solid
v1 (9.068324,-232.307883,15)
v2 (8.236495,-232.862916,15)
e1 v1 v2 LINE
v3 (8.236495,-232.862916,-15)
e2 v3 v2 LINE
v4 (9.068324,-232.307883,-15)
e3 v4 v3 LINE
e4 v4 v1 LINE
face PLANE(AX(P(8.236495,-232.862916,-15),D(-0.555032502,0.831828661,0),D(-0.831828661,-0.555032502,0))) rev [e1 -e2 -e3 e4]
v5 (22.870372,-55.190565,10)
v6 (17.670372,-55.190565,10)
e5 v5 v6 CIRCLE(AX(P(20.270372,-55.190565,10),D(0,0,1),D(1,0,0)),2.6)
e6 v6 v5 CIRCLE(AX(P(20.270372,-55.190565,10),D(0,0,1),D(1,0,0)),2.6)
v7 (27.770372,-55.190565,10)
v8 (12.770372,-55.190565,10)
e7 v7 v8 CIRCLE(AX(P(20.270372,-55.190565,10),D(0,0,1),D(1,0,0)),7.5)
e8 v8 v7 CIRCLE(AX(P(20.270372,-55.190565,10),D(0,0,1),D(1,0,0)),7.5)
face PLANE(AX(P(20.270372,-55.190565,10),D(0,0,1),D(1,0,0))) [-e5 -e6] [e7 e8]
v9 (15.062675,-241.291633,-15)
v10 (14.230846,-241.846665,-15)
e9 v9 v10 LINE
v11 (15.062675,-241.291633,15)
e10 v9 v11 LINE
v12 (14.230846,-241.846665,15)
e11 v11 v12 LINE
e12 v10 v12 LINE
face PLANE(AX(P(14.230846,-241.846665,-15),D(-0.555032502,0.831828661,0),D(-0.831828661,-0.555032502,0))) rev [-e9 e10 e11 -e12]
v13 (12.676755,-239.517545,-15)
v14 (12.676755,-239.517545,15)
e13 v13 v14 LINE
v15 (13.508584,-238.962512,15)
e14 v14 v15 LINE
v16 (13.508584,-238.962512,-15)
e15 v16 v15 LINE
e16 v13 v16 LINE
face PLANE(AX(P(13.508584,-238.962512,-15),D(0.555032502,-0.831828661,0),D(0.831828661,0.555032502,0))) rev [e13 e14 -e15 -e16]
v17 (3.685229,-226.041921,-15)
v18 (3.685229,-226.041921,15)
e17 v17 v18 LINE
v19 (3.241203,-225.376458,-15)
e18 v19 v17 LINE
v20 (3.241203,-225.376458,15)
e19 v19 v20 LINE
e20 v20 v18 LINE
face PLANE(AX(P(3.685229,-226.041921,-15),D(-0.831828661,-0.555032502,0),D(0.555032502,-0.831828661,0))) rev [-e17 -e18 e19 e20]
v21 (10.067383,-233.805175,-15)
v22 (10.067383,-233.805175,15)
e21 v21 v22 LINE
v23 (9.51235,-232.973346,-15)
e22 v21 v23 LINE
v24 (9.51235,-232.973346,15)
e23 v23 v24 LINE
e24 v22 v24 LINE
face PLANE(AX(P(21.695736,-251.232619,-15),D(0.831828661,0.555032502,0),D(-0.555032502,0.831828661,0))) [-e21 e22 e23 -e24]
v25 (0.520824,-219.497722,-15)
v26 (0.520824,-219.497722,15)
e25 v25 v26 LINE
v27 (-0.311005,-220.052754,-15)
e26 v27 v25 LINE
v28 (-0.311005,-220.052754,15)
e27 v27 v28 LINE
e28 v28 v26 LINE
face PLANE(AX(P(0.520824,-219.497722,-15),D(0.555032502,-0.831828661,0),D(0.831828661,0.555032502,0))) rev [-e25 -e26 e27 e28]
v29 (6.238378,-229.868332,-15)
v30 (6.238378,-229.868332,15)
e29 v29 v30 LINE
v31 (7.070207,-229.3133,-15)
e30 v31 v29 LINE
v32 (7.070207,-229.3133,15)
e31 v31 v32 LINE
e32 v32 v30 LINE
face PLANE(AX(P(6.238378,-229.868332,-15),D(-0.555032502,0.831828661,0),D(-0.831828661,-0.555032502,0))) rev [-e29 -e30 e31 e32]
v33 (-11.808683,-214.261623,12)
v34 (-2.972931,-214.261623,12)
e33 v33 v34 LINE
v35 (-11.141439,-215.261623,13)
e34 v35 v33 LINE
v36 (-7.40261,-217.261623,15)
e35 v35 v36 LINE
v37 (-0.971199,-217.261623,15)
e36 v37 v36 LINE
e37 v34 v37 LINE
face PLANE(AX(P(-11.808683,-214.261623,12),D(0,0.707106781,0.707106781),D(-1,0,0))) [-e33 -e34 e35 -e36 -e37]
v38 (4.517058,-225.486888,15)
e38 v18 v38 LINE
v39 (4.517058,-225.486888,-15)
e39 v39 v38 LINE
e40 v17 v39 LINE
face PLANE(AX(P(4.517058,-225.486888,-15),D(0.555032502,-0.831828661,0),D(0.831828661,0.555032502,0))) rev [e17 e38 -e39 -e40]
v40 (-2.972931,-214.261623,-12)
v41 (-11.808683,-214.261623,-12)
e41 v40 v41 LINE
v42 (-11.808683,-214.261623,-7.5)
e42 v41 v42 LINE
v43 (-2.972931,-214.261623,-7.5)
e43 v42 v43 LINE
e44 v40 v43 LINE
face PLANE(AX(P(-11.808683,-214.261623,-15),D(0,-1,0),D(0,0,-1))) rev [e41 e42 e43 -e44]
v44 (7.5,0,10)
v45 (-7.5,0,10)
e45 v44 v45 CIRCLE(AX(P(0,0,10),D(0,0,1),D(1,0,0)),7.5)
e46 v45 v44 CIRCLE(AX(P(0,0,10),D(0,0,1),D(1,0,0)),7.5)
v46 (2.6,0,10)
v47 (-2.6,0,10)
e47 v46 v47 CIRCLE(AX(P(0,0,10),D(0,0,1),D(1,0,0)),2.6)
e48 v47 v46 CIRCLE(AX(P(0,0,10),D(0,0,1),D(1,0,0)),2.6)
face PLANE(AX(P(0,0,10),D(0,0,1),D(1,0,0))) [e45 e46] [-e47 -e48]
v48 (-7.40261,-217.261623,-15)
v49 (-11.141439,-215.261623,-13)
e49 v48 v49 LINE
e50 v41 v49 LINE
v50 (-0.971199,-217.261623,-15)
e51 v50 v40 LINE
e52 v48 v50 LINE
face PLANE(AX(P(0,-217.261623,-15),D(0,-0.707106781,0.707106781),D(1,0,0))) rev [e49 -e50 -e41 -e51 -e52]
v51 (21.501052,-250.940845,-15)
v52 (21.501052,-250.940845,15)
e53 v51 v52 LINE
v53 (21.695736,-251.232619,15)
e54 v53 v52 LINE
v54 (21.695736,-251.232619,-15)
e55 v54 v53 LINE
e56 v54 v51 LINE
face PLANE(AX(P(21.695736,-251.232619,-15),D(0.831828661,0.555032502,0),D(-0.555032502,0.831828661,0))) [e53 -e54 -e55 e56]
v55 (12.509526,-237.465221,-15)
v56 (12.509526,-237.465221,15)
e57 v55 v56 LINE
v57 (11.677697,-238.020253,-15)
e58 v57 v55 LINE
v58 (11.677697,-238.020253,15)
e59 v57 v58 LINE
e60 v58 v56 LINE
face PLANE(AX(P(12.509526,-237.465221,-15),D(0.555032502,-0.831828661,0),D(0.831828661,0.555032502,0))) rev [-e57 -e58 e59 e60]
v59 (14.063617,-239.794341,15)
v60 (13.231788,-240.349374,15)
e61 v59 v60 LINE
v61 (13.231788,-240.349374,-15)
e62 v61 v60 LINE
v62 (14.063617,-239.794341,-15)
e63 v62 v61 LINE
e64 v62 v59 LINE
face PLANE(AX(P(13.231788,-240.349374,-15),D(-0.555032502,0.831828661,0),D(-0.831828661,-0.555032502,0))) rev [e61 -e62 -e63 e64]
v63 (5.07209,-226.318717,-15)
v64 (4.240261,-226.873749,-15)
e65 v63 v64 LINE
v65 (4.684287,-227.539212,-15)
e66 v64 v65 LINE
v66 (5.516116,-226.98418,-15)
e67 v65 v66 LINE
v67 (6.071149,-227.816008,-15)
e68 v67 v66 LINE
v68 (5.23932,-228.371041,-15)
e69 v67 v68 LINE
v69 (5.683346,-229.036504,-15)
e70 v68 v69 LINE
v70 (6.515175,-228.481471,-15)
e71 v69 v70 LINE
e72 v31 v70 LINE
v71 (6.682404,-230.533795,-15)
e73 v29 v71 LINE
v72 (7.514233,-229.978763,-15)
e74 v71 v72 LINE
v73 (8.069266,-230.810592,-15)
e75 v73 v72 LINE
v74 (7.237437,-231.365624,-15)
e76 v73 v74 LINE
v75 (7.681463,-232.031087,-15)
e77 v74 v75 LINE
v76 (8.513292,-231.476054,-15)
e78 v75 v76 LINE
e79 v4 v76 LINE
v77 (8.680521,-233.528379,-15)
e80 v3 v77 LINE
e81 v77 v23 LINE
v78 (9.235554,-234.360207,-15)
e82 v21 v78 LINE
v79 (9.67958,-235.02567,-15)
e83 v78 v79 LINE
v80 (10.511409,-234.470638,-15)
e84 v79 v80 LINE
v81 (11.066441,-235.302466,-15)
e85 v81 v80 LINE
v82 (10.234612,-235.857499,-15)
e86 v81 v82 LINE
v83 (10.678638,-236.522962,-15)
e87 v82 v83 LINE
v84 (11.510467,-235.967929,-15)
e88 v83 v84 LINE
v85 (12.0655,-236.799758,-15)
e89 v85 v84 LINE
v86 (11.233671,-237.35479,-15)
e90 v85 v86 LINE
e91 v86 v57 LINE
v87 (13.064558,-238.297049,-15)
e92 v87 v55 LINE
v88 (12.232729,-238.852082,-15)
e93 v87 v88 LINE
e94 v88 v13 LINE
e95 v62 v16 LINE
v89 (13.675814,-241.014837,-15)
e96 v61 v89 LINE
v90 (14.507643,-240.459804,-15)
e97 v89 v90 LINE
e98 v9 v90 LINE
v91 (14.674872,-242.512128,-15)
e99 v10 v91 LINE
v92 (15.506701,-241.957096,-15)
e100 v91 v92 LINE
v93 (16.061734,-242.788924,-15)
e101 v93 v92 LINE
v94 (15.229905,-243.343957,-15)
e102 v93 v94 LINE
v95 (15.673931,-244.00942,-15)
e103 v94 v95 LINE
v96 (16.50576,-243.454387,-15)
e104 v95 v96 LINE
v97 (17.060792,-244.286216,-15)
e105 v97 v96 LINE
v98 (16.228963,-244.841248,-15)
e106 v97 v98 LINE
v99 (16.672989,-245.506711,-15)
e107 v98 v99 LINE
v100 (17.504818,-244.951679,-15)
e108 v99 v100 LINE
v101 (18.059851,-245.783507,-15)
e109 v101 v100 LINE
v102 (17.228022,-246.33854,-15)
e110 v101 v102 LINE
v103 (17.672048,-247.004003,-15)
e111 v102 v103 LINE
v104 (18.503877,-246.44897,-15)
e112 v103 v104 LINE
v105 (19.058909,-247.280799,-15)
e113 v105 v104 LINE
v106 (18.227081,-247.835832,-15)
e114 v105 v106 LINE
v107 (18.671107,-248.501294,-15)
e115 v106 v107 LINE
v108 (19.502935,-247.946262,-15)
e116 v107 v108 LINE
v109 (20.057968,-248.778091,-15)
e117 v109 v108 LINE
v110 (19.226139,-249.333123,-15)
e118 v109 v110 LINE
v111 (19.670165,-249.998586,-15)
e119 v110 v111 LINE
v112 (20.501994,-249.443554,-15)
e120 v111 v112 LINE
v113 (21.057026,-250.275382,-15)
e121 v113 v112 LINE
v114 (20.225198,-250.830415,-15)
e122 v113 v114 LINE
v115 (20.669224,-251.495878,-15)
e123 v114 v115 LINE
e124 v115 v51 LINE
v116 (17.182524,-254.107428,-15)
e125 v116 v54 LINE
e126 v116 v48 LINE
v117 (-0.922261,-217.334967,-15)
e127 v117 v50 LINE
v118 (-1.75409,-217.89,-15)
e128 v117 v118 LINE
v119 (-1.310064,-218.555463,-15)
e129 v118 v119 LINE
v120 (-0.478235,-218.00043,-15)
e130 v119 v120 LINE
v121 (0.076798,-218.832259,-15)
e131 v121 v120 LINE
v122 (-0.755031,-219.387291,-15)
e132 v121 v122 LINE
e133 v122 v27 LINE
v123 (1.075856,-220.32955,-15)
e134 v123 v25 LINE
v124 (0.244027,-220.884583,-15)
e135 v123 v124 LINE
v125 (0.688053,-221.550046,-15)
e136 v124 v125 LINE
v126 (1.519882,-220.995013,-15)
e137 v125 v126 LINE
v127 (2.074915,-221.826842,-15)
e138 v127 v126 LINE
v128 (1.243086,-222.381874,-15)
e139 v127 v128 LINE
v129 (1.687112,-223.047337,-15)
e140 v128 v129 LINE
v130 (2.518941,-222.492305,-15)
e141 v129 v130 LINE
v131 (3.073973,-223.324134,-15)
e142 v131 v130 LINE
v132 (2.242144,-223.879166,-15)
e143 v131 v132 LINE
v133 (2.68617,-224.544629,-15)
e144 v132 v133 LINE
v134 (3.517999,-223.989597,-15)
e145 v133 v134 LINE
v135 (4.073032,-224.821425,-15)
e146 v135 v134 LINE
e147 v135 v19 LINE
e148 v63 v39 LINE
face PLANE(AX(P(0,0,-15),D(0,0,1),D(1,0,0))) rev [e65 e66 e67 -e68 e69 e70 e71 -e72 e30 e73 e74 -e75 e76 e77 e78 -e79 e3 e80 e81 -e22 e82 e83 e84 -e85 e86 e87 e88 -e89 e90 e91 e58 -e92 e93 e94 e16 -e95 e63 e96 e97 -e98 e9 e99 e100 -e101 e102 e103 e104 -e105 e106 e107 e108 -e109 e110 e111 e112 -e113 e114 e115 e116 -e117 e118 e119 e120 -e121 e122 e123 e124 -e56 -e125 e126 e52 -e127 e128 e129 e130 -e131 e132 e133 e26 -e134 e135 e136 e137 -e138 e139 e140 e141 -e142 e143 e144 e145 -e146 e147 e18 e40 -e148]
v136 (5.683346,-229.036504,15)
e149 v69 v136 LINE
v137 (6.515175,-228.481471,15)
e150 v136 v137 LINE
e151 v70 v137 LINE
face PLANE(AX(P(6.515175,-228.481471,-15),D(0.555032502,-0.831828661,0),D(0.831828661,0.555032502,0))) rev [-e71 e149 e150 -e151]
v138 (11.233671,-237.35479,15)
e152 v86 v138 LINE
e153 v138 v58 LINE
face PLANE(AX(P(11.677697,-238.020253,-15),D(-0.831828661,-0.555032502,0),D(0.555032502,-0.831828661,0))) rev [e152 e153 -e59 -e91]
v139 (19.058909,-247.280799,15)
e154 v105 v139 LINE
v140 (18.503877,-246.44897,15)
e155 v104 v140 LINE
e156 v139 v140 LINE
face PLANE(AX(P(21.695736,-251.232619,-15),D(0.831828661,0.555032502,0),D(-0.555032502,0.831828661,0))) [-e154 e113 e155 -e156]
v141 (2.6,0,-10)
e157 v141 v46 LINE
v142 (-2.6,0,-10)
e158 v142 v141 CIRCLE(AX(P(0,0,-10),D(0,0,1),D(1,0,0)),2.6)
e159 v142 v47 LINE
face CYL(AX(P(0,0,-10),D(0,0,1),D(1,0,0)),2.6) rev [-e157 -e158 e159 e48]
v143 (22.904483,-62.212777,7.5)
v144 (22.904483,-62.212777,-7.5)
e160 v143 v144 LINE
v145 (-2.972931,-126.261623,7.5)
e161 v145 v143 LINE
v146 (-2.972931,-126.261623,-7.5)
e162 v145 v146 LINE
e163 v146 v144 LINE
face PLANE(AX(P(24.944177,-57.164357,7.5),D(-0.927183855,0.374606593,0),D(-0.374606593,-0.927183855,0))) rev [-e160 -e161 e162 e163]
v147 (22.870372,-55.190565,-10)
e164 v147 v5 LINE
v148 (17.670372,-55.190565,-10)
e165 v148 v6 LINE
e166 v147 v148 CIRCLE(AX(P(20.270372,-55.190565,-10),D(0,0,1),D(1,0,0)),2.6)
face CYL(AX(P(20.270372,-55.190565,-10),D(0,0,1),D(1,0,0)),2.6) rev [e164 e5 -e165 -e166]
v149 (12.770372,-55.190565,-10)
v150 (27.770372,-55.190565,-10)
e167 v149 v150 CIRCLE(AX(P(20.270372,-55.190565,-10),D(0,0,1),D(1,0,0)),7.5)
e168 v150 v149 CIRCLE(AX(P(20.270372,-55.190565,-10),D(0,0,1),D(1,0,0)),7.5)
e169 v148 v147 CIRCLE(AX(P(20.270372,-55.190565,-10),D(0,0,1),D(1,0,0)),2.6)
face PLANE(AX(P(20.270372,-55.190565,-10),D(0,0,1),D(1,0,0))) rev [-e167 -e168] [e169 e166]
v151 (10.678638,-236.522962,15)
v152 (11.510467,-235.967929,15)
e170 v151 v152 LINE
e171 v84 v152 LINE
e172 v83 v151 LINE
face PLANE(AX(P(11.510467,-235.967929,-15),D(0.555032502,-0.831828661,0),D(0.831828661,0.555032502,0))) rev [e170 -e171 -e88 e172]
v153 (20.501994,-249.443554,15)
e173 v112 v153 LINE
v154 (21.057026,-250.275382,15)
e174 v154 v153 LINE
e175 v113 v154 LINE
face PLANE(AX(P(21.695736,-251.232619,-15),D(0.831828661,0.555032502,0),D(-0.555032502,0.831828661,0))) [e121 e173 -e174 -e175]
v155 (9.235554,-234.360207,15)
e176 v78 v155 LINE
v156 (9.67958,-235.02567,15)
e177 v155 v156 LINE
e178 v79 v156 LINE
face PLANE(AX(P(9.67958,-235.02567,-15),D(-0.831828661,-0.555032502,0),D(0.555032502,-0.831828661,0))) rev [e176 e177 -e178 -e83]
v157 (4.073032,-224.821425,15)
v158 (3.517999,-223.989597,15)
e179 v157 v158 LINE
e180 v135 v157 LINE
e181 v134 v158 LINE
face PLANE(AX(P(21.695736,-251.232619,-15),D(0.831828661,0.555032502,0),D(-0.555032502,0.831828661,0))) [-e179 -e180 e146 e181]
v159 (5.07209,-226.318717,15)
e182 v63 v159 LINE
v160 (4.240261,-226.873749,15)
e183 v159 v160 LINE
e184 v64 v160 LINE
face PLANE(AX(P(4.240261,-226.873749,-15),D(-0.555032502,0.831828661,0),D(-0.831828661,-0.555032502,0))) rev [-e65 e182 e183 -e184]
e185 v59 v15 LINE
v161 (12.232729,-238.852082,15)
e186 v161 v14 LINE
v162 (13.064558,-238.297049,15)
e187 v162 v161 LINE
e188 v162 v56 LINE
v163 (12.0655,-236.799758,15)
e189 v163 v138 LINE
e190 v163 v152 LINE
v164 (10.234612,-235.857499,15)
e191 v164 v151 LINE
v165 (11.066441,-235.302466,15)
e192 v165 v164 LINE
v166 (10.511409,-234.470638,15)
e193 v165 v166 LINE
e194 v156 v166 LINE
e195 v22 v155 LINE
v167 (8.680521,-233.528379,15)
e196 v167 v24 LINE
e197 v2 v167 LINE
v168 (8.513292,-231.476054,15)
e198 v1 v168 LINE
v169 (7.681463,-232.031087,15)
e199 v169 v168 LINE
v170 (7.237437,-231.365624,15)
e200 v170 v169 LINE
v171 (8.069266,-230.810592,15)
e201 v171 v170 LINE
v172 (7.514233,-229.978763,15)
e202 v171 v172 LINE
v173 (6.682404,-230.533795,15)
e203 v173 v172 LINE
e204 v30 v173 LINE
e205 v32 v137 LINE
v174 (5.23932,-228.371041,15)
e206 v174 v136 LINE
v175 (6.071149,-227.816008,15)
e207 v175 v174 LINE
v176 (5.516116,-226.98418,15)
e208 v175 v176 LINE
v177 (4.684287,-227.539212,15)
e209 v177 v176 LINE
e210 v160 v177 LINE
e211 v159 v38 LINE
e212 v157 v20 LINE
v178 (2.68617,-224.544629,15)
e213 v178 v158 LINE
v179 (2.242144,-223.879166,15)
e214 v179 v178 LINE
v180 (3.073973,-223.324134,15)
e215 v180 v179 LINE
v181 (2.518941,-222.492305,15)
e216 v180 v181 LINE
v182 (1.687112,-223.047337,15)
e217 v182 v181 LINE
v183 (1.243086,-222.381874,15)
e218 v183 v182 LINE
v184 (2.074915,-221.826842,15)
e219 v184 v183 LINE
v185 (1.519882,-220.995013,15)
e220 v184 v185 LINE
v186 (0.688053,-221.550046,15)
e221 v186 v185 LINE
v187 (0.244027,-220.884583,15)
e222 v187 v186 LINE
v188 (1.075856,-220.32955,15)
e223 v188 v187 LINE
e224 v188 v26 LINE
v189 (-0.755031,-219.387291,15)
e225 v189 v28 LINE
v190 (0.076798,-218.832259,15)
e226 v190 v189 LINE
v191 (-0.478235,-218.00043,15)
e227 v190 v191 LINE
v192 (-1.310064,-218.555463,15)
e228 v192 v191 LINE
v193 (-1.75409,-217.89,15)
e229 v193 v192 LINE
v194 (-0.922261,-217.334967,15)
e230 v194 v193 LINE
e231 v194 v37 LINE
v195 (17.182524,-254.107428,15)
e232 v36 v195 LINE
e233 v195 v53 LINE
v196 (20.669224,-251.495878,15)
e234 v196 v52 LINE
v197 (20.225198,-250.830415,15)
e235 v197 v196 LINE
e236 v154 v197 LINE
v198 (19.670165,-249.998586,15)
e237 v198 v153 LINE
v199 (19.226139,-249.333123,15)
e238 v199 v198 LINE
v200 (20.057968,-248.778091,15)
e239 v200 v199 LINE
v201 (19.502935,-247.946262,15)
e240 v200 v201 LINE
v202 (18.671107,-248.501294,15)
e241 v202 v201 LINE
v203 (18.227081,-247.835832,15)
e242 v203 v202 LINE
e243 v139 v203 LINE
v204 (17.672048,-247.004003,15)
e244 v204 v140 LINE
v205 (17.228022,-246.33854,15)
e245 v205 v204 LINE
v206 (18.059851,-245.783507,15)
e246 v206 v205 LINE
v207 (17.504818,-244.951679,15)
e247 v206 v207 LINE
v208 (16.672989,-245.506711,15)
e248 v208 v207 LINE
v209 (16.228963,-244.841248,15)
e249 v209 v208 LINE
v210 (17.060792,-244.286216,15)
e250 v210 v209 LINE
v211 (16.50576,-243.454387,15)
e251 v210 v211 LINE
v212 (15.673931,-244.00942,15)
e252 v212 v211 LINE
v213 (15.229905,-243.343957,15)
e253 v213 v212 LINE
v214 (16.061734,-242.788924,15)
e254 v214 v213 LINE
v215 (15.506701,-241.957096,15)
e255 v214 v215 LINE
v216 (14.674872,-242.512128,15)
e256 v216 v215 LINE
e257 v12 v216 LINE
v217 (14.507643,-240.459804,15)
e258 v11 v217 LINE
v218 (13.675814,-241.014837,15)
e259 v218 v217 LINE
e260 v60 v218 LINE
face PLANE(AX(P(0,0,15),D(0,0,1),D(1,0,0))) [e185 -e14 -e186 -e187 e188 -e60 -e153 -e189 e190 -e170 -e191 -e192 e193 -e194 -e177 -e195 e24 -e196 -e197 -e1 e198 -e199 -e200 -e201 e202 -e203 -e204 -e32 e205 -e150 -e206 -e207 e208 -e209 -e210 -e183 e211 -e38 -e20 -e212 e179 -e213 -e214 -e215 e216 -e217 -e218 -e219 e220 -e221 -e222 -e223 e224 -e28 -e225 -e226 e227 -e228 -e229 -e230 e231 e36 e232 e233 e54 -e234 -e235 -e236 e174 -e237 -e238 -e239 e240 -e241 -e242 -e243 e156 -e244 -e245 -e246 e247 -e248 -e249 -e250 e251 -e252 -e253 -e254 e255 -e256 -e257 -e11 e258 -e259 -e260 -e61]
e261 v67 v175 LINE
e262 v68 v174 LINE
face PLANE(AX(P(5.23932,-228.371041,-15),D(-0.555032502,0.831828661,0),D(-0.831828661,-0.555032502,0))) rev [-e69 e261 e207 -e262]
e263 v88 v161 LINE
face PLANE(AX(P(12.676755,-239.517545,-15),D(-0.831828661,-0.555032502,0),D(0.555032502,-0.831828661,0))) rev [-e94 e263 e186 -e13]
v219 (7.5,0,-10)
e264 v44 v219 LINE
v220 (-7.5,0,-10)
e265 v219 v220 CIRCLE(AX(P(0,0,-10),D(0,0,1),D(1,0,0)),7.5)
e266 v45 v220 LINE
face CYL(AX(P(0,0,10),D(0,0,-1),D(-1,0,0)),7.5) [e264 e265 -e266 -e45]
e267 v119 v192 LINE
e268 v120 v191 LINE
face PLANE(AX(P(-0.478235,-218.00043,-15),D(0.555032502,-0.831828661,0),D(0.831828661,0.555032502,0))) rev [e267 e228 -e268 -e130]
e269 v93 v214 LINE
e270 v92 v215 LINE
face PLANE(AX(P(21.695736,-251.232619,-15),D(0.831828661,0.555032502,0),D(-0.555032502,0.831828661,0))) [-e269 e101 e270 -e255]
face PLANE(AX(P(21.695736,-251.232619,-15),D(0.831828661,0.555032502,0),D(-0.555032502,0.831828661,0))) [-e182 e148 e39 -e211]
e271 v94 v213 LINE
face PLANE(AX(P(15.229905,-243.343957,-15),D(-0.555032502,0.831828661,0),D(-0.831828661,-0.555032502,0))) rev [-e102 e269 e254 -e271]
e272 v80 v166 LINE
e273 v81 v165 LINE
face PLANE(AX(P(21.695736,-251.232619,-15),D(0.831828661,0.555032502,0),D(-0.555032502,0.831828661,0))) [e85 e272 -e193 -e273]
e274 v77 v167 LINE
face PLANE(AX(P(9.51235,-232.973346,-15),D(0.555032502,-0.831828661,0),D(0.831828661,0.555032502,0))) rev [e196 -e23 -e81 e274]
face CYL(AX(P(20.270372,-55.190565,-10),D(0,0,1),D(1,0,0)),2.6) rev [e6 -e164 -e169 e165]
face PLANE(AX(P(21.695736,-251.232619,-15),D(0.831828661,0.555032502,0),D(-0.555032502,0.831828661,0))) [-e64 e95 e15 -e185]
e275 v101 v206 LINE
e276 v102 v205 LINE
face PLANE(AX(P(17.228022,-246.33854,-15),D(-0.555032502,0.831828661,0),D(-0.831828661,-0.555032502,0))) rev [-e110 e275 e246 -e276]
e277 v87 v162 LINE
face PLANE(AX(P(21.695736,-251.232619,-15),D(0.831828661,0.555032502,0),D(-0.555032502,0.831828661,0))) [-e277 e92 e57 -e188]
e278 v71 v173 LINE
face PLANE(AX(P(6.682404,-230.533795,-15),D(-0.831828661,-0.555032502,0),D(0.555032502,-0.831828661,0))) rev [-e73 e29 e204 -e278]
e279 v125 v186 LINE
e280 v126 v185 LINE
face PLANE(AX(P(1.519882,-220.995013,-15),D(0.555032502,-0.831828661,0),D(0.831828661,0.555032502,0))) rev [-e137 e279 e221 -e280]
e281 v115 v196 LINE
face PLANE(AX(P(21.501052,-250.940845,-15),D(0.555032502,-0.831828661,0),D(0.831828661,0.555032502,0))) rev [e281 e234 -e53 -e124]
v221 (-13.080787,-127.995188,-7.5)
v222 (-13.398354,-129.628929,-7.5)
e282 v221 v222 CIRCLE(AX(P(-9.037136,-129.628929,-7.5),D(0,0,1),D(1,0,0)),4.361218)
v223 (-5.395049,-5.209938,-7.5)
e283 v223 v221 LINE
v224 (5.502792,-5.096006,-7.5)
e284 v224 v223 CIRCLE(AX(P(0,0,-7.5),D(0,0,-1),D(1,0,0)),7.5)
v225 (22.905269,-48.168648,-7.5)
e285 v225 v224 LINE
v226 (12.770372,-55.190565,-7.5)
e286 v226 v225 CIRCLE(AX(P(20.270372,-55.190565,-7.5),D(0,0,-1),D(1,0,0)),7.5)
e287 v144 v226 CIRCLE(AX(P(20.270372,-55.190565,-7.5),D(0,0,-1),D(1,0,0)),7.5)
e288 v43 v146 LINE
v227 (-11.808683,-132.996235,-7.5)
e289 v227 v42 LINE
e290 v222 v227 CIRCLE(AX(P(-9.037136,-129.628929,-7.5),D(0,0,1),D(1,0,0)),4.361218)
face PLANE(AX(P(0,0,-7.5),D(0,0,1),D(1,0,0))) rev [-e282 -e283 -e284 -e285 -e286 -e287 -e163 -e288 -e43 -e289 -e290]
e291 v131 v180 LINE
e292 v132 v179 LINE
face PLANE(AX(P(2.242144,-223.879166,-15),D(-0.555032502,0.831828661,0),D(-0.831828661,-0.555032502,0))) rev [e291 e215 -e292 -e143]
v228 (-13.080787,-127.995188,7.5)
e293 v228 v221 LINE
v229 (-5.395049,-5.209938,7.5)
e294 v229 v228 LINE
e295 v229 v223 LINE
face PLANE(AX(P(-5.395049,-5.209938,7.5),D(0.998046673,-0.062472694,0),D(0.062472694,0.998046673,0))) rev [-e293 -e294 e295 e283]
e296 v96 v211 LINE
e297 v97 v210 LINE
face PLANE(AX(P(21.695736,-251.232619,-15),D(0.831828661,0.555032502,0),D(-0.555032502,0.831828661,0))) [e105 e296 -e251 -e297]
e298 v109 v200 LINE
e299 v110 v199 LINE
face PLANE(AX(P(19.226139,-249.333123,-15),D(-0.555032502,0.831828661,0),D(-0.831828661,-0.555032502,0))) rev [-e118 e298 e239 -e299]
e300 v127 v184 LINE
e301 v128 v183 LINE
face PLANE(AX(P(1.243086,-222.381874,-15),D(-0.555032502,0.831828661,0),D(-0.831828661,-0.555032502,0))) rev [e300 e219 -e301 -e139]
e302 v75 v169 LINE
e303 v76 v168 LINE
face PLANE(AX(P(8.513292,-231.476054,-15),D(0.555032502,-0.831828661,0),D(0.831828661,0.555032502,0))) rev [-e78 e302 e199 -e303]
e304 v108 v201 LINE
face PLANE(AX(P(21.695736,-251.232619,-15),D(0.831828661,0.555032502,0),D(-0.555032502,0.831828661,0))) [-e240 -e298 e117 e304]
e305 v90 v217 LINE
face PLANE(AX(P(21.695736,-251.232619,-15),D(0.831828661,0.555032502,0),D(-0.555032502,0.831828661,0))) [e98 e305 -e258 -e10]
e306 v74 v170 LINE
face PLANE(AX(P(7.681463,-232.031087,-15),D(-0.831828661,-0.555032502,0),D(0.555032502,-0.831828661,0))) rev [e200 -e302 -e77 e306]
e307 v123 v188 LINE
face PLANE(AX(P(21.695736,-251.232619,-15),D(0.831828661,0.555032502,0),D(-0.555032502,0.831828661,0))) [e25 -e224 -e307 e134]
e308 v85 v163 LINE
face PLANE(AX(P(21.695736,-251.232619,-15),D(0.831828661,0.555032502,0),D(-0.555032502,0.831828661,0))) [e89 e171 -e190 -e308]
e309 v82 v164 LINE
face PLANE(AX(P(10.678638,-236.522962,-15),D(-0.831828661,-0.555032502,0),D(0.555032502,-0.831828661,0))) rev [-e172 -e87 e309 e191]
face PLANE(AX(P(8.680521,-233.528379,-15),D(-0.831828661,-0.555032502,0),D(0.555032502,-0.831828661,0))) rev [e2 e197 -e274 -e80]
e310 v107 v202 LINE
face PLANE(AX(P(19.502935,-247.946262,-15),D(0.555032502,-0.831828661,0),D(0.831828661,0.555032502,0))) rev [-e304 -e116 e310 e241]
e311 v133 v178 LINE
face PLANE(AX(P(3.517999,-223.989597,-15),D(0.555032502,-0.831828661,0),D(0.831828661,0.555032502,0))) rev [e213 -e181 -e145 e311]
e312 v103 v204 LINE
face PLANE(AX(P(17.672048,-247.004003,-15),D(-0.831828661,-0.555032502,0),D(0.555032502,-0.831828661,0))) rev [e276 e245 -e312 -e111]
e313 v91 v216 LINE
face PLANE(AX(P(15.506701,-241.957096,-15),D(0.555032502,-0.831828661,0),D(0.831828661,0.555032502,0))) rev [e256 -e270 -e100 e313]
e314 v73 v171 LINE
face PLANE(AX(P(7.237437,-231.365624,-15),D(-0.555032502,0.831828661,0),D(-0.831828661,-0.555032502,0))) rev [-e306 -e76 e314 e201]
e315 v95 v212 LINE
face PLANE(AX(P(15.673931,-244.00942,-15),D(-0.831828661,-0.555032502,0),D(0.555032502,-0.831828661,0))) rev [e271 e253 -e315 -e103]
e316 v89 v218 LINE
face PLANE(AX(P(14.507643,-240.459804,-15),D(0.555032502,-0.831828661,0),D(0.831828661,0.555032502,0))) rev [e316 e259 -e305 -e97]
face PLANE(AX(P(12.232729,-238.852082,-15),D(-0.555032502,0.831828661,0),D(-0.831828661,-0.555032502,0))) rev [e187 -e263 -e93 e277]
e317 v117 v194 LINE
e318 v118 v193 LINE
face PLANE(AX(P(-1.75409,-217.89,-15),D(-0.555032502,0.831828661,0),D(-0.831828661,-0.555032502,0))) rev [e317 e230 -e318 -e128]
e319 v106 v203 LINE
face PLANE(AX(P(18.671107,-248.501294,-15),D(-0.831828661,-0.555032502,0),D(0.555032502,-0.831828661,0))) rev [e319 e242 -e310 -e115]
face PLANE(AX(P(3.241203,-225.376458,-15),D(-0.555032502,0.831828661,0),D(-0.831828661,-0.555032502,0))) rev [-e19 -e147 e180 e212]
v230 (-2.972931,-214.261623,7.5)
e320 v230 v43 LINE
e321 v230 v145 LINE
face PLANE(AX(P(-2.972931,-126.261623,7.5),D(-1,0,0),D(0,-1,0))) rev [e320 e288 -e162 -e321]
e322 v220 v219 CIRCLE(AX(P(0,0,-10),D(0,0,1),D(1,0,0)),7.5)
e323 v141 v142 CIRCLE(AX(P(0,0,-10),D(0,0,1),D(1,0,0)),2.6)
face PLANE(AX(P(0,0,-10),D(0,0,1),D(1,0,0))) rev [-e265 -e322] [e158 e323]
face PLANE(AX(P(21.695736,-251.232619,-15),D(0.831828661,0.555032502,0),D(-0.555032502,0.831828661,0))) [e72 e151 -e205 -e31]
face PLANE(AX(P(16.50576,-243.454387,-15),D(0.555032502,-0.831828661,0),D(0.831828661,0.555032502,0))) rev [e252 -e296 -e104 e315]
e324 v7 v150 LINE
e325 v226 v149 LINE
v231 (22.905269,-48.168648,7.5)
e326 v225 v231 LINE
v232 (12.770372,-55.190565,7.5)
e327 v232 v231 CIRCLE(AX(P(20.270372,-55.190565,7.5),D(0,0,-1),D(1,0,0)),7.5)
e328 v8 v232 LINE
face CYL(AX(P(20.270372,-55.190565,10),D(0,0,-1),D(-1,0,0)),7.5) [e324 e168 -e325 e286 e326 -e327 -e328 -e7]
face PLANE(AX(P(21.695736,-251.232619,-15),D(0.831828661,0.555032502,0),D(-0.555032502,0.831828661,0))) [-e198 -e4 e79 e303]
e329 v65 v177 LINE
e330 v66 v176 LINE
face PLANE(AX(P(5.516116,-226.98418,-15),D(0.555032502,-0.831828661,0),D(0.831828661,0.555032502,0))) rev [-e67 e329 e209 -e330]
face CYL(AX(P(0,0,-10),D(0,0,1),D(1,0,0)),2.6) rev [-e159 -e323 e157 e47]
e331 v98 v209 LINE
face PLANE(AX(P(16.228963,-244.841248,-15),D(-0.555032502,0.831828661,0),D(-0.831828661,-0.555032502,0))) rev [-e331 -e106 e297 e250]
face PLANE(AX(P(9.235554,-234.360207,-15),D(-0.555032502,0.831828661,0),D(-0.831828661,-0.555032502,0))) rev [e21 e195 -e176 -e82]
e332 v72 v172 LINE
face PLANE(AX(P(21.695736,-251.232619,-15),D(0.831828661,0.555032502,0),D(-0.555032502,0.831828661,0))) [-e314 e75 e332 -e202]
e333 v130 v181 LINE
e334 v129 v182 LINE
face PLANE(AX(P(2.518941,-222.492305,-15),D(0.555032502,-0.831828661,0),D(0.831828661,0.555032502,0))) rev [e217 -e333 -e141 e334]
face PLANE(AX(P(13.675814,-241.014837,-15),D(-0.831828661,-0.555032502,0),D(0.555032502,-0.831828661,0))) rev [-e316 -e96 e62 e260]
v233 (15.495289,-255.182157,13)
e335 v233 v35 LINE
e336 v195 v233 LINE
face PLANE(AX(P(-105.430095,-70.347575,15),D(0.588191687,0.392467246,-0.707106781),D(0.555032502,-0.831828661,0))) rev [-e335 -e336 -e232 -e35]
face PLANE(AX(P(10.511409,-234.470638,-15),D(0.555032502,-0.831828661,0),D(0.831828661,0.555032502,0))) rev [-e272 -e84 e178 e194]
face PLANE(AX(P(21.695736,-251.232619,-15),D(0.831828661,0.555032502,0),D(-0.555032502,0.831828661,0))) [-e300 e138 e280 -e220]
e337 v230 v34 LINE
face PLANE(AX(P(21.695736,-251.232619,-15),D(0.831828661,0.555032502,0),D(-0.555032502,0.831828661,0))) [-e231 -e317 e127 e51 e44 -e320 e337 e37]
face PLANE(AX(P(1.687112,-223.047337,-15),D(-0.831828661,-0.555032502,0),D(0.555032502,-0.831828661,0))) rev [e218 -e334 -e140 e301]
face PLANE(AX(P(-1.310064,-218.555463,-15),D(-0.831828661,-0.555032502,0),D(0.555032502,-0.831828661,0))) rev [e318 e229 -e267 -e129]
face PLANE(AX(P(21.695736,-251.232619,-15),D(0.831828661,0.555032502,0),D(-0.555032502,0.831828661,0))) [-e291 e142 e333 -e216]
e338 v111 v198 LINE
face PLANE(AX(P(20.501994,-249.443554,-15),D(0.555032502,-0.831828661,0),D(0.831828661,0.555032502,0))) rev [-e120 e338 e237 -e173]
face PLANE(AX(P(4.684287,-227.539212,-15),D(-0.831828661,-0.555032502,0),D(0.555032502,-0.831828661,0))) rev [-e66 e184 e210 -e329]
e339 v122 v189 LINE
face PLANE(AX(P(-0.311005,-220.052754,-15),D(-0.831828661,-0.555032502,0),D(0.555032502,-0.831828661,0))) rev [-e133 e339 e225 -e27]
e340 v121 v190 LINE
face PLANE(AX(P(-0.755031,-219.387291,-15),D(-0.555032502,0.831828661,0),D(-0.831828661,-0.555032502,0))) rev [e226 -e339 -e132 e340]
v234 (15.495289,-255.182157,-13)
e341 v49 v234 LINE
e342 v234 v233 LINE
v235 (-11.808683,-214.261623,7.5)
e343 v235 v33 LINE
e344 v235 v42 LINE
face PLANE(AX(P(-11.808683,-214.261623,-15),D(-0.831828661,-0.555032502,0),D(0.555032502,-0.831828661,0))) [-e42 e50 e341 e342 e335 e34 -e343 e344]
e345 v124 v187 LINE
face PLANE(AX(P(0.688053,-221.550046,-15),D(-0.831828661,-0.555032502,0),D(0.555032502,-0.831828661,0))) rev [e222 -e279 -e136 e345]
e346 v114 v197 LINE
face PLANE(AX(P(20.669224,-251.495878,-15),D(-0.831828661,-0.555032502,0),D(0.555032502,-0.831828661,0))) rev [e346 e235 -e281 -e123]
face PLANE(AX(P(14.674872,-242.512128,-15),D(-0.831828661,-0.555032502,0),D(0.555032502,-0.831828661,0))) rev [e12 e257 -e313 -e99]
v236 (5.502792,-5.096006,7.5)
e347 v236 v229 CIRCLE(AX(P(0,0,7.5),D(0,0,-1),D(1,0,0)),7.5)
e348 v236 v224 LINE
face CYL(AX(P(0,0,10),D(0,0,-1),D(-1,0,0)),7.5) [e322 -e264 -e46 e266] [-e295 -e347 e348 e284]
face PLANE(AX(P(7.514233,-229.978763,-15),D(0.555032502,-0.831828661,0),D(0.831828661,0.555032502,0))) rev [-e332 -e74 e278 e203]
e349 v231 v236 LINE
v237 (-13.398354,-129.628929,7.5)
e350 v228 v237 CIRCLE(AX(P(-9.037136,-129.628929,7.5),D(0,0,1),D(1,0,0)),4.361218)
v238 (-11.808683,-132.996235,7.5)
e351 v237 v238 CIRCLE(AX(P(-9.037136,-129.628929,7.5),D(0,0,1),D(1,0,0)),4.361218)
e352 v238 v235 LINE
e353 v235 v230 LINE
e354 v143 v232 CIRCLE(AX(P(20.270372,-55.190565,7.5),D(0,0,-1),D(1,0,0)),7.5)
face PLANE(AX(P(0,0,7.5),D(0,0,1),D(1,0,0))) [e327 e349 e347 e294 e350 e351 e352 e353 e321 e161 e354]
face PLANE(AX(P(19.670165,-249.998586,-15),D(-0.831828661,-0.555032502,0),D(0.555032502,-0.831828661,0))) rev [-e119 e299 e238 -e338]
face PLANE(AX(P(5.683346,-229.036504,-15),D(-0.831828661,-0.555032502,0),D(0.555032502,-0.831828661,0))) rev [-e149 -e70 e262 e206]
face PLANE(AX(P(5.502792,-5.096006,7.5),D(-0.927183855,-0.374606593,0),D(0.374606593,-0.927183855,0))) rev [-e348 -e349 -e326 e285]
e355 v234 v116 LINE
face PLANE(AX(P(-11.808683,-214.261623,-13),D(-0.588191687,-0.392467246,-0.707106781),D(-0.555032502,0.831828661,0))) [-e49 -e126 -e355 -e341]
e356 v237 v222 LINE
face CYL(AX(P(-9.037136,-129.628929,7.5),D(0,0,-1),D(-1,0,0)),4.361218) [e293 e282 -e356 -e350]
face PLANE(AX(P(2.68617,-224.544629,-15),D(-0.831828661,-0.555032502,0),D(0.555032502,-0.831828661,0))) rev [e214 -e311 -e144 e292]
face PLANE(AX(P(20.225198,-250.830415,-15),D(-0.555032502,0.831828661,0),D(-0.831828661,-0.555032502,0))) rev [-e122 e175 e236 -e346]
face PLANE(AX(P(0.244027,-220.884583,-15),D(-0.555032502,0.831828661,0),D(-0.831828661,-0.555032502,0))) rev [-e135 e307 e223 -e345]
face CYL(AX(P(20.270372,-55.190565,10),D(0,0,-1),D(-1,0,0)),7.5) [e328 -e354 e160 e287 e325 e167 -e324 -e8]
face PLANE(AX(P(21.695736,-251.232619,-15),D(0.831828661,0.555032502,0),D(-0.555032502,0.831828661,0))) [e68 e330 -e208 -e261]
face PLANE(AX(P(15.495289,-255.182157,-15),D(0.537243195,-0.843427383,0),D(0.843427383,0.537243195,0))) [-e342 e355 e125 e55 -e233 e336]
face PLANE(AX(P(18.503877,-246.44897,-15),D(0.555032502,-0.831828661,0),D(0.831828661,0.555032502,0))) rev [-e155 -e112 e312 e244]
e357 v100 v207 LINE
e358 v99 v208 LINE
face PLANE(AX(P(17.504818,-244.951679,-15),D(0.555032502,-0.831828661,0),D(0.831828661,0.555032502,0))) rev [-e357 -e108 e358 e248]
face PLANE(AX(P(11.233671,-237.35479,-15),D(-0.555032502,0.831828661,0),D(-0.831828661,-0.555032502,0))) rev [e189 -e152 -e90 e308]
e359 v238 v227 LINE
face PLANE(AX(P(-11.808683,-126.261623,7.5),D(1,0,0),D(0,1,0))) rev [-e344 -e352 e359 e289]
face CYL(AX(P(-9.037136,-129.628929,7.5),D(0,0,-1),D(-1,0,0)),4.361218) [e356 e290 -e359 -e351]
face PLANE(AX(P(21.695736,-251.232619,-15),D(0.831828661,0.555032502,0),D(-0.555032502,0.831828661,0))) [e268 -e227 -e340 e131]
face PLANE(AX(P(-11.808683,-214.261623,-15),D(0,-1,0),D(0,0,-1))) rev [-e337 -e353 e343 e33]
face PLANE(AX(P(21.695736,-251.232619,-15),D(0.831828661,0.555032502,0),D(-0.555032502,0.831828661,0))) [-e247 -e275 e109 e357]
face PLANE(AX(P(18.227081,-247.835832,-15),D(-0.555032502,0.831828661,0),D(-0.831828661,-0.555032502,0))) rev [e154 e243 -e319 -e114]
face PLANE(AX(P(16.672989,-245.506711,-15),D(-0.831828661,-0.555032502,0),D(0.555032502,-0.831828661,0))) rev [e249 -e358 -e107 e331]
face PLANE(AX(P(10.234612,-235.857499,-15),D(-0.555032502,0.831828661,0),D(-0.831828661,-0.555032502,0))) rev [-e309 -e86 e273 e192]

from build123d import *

# Parameters (mm, degrees)
SKETCH1_R            = 7.5
BOSS_EXTRUDE1_DEPTH  = 10
BOSS_EXTRUDE2_DEPTH  = 7.5
SKETCH3_R            = 2.6
CUT_EXTRUDE1_DEPTH   = 69.367154188
BOSS_EXTRUDE3_DEPTH  = 7.5
SKETCH6_R            = 7.5
BOSS_EXTRUDE4_DEPTH  = 10
SKETCH7_R            = 2.6
CUT_EXTRUDE2_DEPTH   = 139.291550533
BOSS_EXTRUDE8_DEPTH  = 7.5
SKETCH16_W           = 8.835752036
SKETCH16_H           = 88
BOSS_EXTRUDE9_DEPTH  = 7.5
BOSS_EXTRUDE10_DEPTH = 15
CHAMFER1_SIZE        = 3
CHAMFER2_SIZE        = 2
CUT_EXTRUDE3_DEPTH   = 259.435923483


with BuildPart() as part:
    # Sketch1 → Boss-Extrude1 (new, symmetric)
    with BuildSketch(Plane.XY):
        Circle(SKETCH1_R)
    extrude(amount=BOSS_EXTRUDE1_DEPTH, both=True)

    # Sketch2 → Boss-Extrude2 (add, symmetric)
    with BuildSketch(Plane.XY):
        with BuildLine():
            Line((5.502792208, -5.096006075), (24.97443042, -53.29000183))
            ThreePointArc((24.97443042, -53.29000183), (22.170934791, -59.894623641), (15.566312979, -57.091128012))
            Line((15.566312979, -57.091128012), (-5.395048503, -5.209937778))
            ThreePointArc((-5.395048503, -5.209937778), (0.078404622, -7.49959017), (5.502792208, -5.096006075))
        make_face()
    extrude(amount=BOSS_EXTRUDE2_DEPTH, both=True)

    # Sketch3 → Cut-Extrude1 (cut, through all)
    with BuildSketch(Plane.XY.offset(10)):
        Circle(SKETCH3_R)
    extrude(amount=-CUT_EXTRUDE1_DEPTH, mode=Mode.SUBTRACT)

    # Sketch5 → Boss-Extrude3 (add, symmetric)
    with BuildSketch(Plane.XY):
        with BuildLine():
            Line((15.566312979, -57.091128012), (-13.08078666, -127.995187718))
            ThreePointArc((-13.08078666, -127.995187718), (-10.670876789, -133.672579589), (-4.993484918, -131.262669718))
            Line((-4.993484918, -131.262669718), (24.944176558, -57.164357377))
            ThreePointArc((24.944176558, -57.164357377), (20.230755301, -60.263901008), (15.566312979, -57.091128012))
        make_face()
    extrude(amount=BOSS_EXTRUDE3_DEPTH, both=True)

    # Sketch6 → Boss-Extrude4 (add, symmetric)
    with BuildSketch(Plane.XY):
        with Locations((20.2703717, -55.190564921)):
            Circle(SKETCH6_R)
    extrude(amount=BOSS_EXTRUDE4_DEPTH, both=True)

    # Sketch7 → Cut-Extrude2 (cut, through all)
    with BuildSketch(Plane.XY.offset(10)):
        with Locations((20.2703717, -55.190564921)):
            Circle(SKETCH7_R)
    extrude(amount=-CUT_EXTRUDE2_DEPTH, mode=Mode.SUBTRACT)

    # Sketch11 → Boss-Extrude8 (add, symmetric)
    with BuildSketch(Plane.XY):
        with BuildLine():
            Line((-5.395048503, -5.209937778), (-13.08078666, -127.995187718))
            Line((-13.08078666, -127.995187718), (14.432076042, -59.898462945))
            ThreePointArc((14.432076042, -59.898462945), (12.821975428, -56.068854724), (13.497151784, -51.969774339))
            Line((13.497151784, -51.969774339), (-5.395048503, -5.209937778))
        make_face()
    extrude(amount=BOSS_EXTRUDE8_DEPTH, both=True)

    # Sketch16 → Boss-Extrude9 (add, symmetric)
    with BuildSketch(Plane.XY):
        with Locations((-7.390806842, -170.261622843)):
            Rectangle(SKETCH16_W, SKETCH16_H)
    extrude(amount=BOSS_EXTRUDE9_DEPTH, both=True)

    # Sketch17 → Boss-Extrude10 (add, symmetric)
    with BuildSketch(Plane(origin=(0, 0, 0), x_dir=(-1, 0, 0), z_dir=(0, 0, -1))):
        Polygon((11.80868286, -214.261622843), (2.972930824, -214.261622843), (-21.695736326, -251.232618801), (-15.495288767, -255.182156512), align=None)
    extrude(amount=BOSS_EXTRUDE10_DEPTH, both=True)

    # Chamfer1
    chamfer1_edges = [part.edges().sort_by_distance(p)[0] for p in [
        (-7.390806842, -214.261622843, 15),
        (-7.390806842, -214.261622843, -15),
    ]]
    chamfer(chamfer1_edges, length=CHAMFER1_SIZE)

    # Chamfer2
    chamfer2_edges = [part.edges().sort_by_distance(p)[0] for p in [
        (2.844168626, -236.221889677, 15),
        (2.844168626, -236.221889677, -15),
    ]]
    chamfer(chamfer2_edges, length=CHAMFER2_SIZE)

    # Sketch18 → Cut-Extrude3 (cut, through all)
    with BuildSketch(Plane.XY.offset(15)):
        Polygon((-0.922260896, -217.334967226), (-0.478234895, -218.000430155), (-1.310063556, -218.555462656), (-1.754089558, -217.889999727), align=None)
        Polygon((-0.755031055, -219.387291318), (0.076797607, -218.832258816), (0.520823608, -219.497721745), (-0.311005053, -220.052754247), align=None)
        Polygon((0.244027448, -220.884582909), (1.07585611, -220.329550407), (1.519882111, -220.995013336), (0.68805345, -221.550045838), align=None)
        Polygon((1.243085951, -222.381874499), (2.074914613, -221.826841998), (2.518940614, -222.492304927), (1.687111953, -223.047337429), align=None)
        Polygon((2.242144454, -223.87916609), (3.073973116, -223.324133588), (3.517999117, -223.989596518), (2.686170456, -224.544629019), align=None)
        Polygon((3.241202957, -225.376457681), (4.073031619, -224.821425179), (4.51705762, -225.486888108), (3.685228959, -226.04192061), align=None)
        Polygon((4.24026146, -226.873749271), (5.072090122, -226.31871677), (5.516116123, -226.984179699), (4.684287462, -227.539212201), align=None)
        Polygon((5.239319963, -228.371040862), (6.071148625, -227.81600836), (6.515174626, -228.48147129), (5.683345965, -229.036503791), align=None)
        Polygon((6.238378466, -229.868332453), (7.070207128, -229.313299951), (7.514233129, -229.97876288), (6.682404468, -230.533795382), align=None)
        Polygon((7.237436969, -231.365624043), (8.069265631, -230.810591542), (8.513291632, -231.476054471), (7.681462971, -232.031086973), align=None)
        Polygon((8.236495472, -232.862915634), (9.068324134, -232.307883132), (9.512350135, -232.973346062), (8.680521474, -233.528378563), align=None)
        Polygon((9.235553975, -234.360207225), (10.067382637, -233.805174723), (10.511408638, -234.470637652), (9.679579977, -235.025670154), align=None)
        Polygon((10.234612478, -235.857498816), (11.06644114, -235.302466314), (11.510467141, -235.967929243), (10.67863848, -236.522961745), align=None)
        Polygon((11.233670981, -237.354790406), (12.065499643, -236.799757905), (12.509525644, -237.465220834), (11.677696983, -238.020253335), align=None)
        Polygon((12.232729484, -238.852081997), (13.064558146, -238.297049495), (13.508584147, -238.962512424), (12.676755486, -239.517544926), align=None)
        Polygon((13.231787987, -240.349373588), (14.063616649, -239.794341086), (14.50764265, -240.459804015), (13.675813989, -241.014836517), align=None)
        Polygon((14.23084649, -241.846665178), (15.062675152, -241.291632677), (15.506701153, -241.957095606), (14.674872492, -242.512128108), align=None)
        Polygon((15.229904993, -243.343956769), (16.061733655, -242.788924267), (16.505759656, -243.454387197), (15.673930995, -244.009419698), align=None)
        Polygon((16.228963496, -244.84124836), (17.060792158, -244.286215858), (17.504818159, -244.951678787), (16.672989498, -245.506711289), align=None)
        Polygon((17.228021999, -246.33853995), (18.059850661, -245.783507449), (18.503876662, -246.448970378), (17.672048001, -247.00400288), align=None)
        Polygon((18.227080502, -247.835831541), (19.058909164, -247.280799039), (19.502935165, -247.946261969), (18.671106504, -248.50129447), align=None)
        Polygon((19.226139005, -249.333123132), (20.057967667, -248.77809063), (20.501993668, -249.443553559), (19.670165007, -249.998586061), align=None)
        Polygon((20.225197509, -250.830414722), (21.05702617, -250.275382221), (21.501052171, -250.94084515), (20.66922351, -251.495877652), align=None)
        Polygon((21.224256012, -252.327706313), (22.056084673, -251.772673811), (22.500110674, -252.438136741), (21.668282013, -252.993169242), align=None)
    extrude(amount=-CUT_EXTRUDE3_DEPTH, mode=Mode.SUBTRACT)


solid = part.part
